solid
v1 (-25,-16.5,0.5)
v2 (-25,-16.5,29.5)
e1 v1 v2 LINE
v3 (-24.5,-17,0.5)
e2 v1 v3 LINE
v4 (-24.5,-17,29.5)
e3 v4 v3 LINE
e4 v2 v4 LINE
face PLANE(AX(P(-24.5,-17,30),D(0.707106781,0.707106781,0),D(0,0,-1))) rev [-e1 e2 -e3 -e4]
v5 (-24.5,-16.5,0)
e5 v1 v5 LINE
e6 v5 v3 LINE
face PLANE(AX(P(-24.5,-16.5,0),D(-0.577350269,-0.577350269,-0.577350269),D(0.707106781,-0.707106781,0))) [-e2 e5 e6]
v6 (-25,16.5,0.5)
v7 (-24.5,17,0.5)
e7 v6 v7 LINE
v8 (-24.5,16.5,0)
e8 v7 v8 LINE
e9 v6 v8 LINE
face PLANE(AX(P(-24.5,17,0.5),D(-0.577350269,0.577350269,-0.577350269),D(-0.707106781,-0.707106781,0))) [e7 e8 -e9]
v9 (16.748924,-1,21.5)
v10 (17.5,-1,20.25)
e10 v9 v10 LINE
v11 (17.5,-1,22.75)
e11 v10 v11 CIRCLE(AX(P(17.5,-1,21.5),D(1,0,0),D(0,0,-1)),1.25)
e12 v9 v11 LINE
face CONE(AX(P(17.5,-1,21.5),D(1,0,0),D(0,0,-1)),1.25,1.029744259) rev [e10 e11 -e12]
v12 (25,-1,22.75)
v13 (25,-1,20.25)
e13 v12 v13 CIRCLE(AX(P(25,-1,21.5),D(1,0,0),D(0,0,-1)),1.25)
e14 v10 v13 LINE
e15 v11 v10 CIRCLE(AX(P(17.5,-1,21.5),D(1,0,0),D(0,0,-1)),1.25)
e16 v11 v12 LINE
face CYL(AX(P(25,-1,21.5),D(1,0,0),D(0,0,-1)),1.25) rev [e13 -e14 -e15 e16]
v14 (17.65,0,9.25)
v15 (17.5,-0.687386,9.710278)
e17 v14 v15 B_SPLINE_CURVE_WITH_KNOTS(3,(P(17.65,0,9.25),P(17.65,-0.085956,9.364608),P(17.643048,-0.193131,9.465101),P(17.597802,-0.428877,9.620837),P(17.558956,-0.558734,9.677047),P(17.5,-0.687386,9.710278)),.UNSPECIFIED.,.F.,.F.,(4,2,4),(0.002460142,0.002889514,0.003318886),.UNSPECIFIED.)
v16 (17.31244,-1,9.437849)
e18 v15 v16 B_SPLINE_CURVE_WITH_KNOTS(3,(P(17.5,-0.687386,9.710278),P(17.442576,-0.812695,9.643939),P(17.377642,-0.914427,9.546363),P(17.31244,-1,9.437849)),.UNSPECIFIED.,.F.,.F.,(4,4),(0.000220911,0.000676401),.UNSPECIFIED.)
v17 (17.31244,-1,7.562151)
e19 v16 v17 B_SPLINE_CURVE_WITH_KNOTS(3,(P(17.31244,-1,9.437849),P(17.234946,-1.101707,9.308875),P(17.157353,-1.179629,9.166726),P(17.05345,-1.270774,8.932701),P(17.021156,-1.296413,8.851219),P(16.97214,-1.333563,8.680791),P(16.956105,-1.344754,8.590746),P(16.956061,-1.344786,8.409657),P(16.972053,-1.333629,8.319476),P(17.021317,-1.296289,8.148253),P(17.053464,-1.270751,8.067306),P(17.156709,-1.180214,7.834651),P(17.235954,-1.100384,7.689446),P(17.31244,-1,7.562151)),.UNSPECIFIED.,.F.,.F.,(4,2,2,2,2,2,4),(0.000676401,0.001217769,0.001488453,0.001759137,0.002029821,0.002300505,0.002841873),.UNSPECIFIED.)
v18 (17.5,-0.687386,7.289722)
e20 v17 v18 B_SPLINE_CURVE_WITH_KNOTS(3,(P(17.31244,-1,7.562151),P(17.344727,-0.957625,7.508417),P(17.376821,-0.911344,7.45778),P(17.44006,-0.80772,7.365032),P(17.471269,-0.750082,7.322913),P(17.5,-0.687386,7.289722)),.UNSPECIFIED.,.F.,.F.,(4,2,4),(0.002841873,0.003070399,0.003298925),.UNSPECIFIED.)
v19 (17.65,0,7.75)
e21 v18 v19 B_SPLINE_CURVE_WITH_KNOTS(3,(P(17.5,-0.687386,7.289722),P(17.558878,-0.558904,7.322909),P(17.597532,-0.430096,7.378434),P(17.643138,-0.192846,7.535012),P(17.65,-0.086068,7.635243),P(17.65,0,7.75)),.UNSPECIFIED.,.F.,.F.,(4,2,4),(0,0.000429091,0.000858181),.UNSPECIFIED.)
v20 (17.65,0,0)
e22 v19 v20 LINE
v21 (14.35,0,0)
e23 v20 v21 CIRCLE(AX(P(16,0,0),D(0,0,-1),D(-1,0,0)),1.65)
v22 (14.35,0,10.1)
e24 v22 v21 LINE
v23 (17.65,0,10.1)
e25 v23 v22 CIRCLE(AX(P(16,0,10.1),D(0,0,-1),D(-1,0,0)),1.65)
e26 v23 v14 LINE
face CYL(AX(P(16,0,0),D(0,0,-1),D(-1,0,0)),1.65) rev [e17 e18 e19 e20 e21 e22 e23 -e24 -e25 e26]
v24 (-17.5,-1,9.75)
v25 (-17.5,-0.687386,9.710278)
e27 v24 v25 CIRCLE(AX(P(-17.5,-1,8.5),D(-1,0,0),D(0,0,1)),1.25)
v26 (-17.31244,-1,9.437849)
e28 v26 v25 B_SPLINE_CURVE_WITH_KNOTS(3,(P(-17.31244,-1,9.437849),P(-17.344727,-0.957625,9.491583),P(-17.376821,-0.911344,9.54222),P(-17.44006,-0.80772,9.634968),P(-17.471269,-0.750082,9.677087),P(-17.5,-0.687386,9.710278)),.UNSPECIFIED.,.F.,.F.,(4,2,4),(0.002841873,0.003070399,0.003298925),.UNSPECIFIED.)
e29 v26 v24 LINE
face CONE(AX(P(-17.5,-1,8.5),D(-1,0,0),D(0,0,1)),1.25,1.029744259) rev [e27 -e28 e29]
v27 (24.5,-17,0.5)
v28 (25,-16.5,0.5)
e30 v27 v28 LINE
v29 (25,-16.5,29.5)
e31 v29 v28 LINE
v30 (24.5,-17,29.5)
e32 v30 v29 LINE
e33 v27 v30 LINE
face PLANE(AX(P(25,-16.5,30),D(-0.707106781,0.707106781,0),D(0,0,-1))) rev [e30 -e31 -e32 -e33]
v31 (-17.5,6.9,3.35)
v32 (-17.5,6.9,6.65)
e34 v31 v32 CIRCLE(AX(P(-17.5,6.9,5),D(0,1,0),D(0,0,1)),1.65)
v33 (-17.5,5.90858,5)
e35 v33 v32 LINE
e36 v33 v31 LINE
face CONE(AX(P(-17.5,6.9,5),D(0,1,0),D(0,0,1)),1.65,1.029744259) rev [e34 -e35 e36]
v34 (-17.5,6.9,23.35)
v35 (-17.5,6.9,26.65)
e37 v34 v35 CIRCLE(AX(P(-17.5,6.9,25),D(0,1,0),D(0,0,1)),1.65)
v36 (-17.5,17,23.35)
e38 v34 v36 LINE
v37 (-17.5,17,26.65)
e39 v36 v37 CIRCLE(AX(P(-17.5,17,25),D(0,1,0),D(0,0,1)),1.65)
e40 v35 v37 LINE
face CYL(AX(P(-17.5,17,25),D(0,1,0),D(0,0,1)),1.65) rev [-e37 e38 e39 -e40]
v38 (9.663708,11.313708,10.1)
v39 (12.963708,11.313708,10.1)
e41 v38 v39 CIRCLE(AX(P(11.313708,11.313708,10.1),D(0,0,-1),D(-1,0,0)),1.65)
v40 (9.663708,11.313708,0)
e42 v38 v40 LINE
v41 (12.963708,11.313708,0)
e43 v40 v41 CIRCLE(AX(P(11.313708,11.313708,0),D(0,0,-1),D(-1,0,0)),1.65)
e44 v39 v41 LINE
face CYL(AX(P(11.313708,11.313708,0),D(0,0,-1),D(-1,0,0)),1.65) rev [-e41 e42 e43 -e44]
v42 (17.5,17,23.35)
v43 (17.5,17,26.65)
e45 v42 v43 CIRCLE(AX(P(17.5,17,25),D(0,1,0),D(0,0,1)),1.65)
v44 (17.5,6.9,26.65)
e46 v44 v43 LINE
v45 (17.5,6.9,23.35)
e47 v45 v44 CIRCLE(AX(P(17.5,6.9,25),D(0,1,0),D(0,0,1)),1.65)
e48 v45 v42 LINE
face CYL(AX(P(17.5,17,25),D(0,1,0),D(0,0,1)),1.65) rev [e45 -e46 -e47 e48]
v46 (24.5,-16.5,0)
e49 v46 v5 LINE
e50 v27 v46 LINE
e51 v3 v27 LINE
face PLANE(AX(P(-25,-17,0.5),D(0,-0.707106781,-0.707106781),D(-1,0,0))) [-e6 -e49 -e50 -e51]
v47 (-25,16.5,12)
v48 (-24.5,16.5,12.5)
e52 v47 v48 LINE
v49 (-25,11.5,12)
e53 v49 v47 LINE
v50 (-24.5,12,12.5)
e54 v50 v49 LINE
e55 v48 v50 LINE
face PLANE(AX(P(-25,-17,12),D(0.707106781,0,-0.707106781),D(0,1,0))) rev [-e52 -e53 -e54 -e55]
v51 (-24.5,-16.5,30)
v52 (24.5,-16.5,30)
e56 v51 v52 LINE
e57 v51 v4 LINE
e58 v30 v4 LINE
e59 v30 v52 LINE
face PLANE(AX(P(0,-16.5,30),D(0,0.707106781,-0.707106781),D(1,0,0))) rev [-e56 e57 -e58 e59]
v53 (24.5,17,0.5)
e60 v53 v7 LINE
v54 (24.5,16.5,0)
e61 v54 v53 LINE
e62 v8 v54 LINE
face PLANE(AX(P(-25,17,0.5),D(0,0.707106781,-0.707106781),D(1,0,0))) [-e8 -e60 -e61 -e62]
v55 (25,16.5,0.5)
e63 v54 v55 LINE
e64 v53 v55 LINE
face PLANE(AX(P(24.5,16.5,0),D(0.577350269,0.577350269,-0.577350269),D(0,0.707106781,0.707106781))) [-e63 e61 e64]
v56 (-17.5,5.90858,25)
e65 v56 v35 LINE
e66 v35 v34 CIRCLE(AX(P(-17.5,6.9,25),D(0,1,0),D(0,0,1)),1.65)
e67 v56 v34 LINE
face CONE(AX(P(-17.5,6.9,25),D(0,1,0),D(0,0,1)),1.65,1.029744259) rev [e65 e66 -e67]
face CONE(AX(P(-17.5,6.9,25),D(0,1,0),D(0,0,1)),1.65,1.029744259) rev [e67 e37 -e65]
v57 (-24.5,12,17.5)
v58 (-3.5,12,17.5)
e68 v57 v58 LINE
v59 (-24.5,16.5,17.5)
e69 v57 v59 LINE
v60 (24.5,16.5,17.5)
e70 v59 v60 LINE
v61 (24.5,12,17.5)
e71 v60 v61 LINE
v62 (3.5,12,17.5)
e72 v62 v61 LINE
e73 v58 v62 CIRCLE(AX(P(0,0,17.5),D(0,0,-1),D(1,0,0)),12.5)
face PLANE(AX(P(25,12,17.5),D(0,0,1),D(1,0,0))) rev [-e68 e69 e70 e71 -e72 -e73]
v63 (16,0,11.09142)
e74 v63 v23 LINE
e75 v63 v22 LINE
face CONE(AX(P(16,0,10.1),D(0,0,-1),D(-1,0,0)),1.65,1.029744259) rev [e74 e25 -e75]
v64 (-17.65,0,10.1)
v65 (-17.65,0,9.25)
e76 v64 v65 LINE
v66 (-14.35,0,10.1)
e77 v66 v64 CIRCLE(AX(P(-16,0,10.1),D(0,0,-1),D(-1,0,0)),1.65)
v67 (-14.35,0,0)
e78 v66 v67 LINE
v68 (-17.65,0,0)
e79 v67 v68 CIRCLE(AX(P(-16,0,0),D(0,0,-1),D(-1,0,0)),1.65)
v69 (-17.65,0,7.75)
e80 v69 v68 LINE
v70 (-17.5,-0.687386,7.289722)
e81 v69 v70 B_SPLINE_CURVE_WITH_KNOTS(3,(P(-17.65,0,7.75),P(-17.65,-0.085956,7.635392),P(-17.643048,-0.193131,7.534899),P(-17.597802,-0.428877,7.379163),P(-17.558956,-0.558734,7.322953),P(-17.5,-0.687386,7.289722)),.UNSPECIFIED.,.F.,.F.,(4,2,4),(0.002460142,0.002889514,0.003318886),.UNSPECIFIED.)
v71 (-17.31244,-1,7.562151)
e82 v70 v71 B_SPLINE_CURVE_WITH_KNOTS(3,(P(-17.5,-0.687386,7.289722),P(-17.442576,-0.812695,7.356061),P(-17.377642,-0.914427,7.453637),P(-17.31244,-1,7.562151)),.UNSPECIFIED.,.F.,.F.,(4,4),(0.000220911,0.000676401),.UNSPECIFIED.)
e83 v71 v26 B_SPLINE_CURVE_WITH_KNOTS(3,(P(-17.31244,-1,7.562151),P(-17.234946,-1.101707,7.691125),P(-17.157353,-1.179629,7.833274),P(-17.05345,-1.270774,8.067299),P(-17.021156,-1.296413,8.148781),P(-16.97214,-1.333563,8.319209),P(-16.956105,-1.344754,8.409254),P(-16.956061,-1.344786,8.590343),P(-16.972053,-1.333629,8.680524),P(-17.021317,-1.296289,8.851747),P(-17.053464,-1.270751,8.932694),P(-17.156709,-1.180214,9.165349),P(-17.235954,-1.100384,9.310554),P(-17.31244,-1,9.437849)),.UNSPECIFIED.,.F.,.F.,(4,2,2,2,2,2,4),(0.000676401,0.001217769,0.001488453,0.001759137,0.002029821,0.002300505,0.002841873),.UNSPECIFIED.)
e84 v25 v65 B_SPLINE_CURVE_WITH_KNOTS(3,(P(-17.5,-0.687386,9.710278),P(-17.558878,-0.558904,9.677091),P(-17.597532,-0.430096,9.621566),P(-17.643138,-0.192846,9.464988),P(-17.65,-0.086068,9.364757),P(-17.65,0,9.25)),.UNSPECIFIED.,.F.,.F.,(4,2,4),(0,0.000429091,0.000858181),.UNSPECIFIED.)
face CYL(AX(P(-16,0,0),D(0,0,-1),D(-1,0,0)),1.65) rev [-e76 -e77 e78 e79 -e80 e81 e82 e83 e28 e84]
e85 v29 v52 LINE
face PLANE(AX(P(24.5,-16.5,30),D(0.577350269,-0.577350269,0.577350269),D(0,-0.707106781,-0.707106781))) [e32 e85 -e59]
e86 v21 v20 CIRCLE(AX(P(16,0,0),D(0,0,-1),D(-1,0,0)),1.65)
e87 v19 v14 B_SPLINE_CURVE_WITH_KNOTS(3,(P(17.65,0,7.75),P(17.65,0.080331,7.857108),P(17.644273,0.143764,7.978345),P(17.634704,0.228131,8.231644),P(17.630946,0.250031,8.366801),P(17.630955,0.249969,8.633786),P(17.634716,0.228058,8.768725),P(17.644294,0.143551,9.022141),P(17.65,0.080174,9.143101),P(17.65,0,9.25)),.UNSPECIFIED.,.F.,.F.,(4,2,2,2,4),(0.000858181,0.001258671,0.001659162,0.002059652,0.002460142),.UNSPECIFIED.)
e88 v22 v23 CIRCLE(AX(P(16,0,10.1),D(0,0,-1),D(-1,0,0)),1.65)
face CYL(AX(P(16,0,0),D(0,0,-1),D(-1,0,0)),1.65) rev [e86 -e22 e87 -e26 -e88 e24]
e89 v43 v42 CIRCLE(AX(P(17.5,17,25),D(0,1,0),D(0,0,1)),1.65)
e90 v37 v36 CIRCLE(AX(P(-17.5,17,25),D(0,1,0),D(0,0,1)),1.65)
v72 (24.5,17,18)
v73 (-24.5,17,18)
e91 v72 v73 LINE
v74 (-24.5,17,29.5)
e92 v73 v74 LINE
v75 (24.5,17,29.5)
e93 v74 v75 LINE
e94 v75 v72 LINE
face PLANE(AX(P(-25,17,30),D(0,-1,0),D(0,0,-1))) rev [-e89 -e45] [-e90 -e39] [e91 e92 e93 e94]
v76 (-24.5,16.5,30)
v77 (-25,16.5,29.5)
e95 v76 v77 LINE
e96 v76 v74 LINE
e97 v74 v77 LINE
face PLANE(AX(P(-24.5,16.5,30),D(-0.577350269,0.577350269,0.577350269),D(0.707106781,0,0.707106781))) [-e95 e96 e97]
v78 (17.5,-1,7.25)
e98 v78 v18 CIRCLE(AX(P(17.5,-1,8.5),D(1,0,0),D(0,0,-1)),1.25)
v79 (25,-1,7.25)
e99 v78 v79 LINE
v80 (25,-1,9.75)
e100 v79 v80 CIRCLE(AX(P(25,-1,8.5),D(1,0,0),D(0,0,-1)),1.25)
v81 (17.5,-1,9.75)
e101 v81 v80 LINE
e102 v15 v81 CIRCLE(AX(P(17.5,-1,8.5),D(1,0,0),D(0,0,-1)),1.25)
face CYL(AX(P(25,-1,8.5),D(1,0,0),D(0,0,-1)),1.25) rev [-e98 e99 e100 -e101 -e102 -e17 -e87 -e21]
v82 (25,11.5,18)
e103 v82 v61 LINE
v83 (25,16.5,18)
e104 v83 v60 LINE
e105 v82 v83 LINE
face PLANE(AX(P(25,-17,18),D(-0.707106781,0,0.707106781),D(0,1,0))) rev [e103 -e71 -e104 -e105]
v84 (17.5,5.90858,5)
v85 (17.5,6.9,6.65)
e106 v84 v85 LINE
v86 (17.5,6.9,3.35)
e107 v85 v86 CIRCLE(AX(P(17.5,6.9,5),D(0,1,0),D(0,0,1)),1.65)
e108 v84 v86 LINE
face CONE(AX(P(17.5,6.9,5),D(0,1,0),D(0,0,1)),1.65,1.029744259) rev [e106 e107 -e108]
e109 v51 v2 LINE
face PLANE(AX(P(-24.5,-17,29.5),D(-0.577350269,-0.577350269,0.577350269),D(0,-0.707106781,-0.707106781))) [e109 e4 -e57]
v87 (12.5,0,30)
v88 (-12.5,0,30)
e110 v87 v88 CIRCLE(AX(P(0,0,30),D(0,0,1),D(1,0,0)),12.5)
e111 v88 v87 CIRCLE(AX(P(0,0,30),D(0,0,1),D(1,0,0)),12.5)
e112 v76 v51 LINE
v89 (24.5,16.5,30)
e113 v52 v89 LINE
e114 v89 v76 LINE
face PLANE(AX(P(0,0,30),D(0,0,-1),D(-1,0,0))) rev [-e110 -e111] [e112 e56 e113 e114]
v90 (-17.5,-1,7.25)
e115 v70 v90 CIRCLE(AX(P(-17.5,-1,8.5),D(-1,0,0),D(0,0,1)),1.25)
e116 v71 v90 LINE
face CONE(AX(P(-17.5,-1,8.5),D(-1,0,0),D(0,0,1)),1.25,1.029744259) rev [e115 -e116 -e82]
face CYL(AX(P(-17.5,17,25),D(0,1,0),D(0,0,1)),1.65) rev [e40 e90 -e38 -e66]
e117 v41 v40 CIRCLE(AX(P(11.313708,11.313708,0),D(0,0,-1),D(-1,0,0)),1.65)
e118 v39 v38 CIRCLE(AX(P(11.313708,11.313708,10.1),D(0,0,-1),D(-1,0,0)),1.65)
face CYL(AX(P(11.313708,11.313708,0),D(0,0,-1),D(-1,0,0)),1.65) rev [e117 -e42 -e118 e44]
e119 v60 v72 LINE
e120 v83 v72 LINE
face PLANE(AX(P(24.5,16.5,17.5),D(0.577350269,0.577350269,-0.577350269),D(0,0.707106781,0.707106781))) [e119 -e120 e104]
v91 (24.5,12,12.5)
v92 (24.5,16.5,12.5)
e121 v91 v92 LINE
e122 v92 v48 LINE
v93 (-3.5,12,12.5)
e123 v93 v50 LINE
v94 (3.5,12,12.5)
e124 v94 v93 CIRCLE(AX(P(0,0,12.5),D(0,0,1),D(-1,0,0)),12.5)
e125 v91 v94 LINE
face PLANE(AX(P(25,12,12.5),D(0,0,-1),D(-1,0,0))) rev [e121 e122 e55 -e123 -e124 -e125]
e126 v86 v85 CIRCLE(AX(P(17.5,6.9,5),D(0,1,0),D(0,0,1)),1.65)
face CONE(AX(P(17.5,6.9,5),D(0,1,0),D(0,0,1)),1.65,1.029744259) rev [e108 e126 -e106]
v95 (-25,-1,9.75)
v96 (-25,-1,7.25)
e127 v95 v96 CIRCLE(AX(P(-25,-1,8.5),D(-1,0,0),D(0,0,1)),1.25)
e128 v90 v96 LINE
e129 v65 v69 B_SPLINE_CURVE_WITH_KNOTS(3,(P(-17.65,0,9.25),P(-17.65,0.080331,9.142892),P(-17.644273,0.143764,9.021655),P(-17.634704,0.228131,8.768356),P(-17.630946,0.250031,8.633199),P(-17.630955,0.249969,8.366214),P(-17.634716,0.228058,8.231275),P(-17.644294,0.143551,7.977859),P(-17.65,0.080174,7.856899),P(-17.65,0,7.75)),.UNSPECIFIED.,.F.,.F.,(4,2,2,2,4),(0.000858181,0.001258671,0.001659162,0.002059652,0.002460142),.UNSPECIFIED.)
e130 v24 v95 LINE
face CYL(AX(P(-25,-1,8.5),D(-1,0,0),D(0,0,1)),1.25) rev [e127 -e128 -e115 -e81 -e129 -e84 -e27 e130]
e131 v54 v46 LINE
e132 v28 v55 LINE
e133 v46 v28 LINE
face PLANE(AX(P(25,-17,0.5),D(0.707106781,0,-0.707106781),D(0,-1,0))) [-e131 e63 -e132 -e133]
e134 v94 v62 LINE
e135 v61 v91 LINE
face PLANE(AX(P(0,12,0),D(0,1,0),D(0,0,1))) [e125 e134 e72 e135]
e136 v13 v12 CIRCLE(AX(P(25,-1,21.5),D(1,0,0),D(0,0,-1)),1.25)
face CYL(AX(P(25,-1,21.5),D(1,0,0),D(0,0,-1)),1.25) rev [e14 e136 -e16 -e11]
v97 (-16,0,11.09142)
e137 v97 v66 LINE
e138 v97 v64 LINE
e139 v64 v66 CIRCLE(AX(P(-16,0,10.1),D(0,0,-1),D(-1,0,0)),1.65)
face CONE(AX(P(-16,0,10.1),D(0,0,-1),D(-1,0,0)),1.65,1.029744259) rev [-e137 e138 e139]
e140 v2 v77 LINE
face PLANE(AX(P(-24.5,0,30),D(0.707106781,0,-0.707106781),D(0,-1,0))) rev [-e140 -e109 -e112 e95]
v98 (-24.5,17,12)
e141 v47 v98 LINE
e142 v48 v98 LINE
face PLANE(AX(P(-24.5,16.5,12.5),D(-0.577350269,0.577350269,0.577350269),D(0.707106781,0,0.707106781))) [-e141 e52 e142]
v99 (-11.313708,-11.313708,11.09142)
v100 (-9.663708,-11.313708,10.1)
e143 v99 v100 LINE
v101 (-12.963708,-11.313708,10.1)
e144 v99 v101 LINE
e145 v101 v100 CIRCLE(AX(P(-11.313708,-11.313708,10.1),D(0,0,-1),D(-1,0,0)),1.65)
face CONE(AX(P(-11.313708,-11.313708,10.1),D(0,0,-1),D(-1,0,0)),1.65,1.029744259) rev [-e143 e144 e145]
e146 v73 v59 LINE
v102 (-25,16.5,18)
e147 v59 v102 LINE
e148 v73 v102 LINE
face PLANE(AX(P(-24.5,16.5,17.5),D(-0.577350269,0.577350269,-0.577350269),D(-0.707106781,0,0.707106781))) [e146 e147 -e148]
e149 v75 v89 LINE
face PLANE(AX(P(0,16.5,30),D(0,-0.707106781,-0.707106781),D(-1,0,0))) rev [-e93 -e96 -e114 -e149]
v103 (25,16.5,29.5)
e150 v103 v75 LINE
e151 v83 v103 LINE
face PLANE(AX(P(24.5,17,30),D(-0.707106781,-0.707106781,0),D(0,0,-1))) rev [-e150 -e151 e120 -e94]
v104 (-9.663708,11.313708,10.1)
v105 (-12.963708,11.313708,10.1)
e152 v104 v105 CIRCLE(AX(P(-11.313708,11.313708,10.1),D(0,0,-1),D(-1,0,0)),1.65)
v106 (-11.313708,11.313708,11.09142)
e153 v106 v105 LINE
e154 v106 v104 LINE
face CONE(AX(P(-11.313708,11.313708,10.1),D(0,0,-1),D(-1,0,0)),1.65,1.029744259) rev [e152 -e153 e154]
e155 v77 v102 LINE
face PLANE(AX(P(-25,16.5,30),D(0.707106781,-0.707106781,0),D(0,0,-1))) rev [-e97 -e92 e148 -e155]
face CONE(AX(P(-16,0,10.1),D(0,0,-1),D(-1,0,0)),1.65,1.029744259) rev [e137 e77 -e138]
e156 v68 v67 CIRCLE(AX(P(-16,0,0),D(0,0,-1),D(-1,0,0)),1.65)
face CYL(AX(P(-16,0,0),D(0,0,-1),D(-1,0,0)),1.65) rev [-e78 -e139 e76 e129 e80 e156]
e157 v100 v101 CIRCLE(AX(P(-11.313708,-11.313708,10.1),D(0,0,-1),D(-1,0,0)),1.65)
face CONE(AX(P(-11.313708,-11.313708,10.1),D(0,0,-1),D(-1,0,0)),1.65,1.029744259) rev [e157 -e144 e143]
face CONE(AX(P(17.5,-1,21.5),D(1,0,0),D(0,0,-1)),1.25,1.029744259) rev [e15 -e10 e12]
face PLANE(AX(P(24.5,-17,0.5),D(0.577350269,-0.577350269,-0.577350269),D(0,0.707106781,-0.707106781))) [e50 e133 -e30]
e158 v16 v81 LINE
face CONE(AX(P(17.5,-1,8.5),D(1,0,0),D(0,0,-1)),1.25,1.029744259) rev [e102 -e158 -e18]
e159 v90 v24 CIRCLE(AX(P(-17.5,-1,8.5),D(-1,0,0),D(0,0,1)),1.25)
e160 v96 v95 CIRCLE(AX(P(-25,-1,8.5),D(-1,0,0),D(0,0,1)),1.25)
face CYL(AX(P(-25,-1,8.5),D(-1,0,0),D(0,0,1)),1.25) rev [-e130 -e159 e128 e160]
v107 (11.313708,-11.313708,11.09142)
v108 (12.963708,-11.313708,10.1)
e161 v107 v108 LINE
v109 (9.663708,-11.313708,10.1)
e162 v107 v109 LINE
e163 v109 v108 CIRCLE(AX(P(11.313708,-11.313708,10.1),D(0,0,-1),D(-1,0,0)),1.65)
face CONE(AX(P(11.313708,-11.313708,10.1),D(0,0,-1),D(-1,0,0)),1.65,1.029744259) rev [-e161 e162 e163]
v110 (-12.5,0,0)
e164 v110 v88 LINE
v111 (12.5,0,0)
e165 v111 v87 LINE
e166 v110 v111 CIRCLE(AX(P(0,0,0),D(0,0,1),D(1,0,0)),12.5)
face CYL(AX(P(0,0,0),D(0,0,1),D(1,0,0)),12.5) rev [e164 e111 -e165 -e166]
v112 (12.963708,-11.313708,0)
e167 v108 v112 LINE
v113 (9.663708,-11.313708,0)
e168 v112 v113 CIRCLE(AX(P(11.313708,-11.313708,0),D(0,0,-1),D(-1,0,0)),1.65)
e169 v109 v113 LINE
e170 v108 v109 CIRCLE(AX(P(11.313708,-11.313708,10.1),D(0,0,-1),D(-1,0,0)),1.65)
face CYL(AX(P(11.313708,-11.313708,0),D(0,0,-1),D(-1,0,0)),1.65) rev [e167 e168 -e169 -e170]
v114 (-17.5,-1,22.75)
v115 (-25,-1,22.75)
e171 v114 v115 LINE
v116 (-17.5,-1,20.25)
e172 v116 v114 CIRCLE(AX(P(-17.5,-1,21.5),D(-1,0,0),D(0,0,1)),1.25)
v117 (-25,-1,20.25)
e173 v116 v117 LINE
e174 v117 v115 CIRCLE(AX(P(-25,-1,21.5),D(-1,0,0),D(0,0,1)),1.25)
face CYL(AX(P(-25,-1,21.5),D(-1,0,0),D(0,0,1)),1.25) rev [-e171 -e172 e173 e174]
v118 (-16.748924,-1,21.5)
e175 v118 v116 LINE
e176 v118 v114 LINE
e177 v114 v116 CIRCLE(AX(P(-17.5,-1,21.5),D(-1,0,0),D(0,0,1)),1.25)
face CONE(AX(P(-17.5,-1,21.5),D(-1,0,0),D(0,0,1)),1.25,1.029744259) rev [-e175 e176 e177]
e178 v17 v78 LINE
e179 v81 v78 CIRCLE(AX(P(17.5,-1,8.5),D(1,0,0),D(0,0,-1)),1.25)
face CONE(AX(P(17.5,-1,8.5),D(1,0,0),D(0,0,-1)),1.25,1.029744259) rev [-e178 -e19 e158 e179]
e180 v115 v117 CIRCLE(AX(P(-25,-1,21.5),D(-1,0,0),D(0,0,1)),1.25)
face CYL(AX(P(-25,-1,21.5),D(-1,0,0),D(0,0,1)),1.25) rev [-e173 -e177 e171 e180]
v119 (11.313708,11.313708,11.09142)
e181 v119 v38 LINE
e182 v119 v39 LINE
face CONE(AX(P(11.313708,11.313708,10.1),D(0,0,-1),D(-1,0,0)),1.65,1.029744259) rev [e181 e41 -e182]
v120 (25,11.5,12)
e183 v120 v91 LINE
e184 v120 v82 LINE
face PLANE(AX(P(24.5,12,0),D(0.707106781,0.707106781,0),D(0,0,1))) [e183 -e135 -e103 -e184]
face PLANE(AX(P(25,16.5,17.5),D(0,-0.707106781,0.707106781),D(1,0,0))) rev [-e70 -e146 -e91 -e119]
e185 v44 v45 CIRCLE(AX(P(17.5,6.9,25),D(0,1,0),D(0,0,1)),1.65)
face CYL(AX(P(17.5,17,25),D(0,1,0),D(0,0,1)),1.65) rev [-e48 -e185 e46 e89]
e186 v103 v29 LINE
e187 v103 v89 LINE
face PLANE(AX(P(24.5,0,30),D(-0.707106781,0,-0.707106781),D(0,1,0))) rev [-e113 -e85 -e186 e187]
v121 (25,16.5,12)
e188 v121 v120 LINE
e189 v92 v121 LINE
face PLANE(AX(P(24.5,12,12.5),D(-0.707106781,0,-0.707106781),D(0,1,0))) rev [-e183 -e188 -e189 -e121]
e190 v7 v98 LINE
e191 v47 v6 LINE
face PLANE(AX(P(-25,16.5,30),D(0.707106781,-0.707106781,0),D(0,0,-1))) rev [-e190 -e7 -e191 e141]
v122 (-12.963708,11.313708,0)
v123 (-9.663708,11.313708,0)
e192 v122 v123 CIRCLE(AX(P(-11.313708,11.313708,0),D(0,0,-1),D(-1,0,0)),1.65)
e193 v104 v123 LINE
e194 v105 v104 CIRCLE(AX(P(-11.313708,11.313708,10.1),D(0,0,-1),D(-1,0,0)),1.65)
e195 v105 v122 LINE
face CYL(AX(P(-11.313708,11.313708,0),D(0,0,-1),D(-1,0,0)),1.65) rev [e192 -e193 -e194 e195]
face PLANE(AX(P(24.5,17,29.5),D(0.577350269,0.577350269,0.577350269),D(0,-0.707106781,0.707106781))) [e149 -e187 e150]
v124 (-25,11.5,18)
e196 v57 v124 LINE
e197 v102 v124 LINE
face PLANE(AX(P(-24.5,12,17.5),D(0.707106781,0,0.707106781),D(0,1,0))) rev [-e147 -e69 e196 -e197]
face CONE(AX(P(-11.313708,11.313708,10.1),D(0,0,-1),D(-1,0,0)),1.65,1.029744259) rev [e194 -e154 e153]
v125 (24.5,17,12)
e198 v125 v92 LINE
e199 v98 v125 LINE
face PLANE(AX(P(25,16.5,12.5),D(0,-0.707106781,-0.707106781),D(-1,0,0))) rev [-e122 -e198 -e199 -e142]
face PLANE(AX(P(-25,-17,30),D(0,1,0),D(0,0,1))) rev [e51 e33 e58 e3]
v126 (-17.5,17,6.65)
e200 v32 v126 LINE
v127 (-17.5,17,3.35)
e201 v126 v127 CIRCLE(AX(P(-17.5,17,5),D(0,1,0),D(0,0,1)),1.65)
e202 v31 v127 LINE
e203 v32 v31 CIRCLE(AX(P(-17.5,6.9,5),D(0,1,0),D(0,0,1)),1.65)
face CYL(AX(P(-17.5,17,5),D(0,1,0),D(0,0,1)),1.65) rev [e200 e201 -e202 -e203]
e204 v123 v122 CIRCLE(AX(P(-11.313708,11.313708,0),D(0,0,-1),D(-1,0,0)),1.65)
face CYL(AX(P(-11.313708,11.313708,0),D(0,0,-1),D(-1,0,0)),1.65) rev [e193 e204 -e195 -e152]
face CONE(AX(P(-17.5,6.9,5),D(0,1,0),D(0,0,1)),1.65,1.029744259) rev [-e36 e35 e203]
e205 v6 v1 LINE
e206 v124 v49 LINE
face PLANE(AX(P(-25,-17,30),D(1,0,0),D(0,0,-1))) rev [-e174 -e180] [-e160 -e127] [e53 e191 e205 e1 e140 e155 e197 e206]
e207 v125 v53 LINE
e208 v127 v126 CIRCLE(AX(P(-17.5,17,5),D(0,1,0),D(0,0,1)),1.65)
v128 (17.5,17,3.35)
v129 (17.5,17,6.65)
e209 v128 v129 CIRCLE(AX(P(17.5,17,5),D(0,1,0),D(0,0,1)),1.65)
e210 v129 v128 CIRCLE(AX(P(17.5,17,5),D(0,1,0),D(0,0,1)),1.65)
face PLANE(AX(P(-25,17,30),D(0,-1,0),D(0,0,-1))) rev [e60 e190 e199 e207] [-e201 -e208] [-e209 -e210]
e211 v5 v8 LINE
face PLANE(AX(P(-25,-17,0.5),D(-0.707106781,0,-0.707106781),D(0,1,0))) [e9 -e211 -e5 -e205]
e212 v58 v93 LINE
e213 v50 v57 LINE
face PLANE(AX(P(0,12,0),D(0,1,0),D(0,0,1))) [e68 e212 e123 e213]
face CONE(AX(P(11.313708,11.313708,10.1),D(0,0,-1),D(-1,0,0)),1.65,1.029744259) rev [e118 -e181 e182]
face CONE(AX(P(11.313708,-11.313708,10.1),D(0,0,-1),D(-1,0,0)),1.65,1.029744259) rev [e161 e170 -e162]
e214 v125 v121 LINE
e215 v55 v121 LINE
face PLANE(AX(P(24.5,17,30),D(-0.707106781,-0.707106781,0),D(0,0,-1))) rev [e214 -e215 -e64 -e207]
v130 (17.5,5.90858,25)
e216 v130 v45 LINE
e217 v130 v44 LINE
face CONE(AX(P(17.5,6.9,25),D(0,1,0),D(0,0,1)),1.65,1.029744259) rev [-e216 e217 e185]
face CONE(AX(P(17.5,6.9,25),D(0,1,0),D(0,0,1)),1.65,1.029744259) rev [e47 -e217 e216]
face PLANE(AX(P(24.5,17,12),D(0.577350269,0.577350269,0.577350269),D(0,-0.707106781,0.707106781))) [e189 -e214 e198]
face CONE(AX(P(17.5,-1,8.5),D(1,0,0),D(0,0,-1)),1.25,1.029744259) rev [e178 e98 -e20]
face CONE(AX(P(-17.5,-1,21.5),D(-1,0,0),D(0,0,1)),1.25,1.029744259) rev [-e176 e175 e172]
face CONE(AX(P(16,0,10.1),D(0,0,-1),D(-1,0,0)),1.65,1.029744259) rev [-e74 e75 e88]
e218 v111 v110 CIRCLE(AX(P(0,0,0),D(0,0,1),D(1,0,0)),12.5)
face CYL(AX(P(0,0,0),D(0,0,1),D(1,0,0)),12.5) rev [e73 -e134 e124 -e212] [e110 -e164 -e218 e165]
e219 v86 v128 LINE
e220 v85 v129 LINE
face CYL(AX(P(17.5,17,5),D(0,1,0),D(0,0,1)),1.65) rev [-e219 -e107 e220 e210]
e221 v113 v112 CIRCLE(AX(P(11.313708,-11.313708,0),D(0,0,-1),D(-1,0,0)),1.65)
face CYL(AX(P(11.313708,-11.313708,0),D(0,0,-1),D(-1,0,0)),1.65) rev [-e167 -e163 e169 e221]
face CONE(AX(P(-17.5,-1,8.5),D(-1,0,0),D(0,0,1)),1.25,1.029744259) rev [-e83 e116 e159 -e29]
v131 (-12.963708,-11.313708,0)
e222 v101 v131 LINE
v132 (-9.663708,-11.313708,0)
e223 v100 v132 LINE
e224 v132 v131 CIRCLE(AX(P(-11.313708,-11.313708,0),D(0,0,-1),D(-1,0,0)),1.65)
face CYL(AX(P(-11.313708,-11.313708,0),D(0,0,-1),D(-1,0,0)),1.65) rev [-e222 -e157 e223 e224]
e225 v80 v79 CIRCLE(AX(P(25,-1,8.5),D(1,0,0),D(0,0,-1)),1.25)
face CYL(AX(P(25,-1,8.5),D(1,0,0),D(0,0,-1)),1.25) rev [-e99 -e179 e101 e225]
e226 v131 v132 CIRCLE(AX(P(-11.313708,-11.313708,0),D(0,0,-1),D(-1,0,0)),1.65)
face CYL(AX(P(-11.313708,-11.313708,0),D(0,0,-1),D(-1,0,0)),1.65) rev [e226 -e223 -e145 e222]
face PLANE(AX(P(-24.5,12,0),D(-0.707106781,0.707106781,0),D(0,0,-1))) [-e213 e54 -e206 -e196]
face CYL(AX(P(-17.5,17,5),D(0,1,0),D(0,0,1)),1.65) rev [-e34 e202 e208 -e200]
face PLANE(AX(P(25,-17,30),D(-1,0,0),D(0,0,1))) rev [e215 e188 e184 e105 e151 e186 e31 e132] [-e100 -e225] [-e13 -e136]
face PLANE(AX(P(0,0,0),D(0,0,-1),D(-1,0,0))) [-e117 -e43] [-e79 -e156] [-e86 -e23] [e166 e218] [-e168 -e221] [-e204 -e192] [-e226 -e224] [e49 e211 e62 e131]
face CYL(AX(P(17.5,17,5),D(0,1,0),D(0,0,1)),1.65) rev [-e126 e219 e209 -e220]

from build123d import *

# Parameters (mm, degrees)
SKETCH_1_W                  = 50
SKETCH_1_H                  = 34
EXTRUDE_1_DEPTH             = 30
HOLE_WIZARD_M4_1_D          = 3.3
HOLE_WIZARD_M4_1_DEPTH      = 10.1
HOLE_WIZARD_M4_1_TIP        = 0.991420021
HOLE_WIZARD_M3_1_AT_2_COUNT = 2
HOLE_WIZARD_M3_1_AT_2_PITCH = 13
SKETCH_15_R                 = 12.5
CUT_EXTRUDE_1_DEPTH         = 43.591079007
HOLE_WIZARD_M4_2_D          = 3.3
HOLE_WIZARD_M4_2_DEPTH      = 10.1
HOLE_WIZARD_M4_2_TIP        = 0.991420021
SKETCH_18_W                 = 50
SKETCH_18_H                 = 5
CUT_EXTRUDE_2_DEPTH         = 5
CHAMFER_1_SIZE              = 0.5


with BuildPart() as part:
    # 草图1 → 凸台-拉伸1 (new body)
    with BuildSketch(Plane.XY):
        Rectangle(SKETCH_1_W, SKETCH_1_H)
    extrude(amount=EXTRUDE_1_DEPTH)

    # M4 螺纹孔1
    with Locations(Plane(origin=(0, 0, 0), x_dir=(-1, 0, 0), z_dir=(0, 0, -1))):
        with Locations((-11.313708499, -11.313708499), (-16, 0), (-11.313708499, 11.313708499), (11.313708499, 11.313708499), (16, 0), (11.313708499, -11.313708499)):
            Hole(HOLE_WIZARD_M4_1_D / 2, depth=HOLE_WIZARD_M4_1_DEPTH)
            with Locations((0, 0, -(HOLE_WIZARD_M4_1_DEPTH + HOLE_WIZARD_M4_1_TIP / 2))):  # 118° drill point
                Cone(0, HOLE_WIZARD_M4_1_D / 2, HOLE_WIZARD_M4_1_TIP, mode=Mode.SUBTRACT)

    # 草图12 → M3 螺纹孔1 (revolve, cut)
    with BuildSketch(Plane(origin=(-25, -1, 8.5), x_dir=(0, 0, 1), z_dir=(0, 1, 0))):
        Polygon((0, 0), (0, 8.251075774), (1.25, 7.5), (1.25, 0), align=None)
    hole_wizard_m3_1 = revolve(axis=Axis((-31.35, -1, 8.5), (1, 0, 0)), mode=Mode.SUBTRACT)

    # M3 螺纹孔1 at 2: M3 螺纹孔1 ×2
    with Locations(*[(0, 0, i * HOLE_WIZARD_M3_1_AT_2_PITCH) for i in range(1, HOLE_WIZARD_M3_1_AT_2_COUNT)]):
        add(hole_wizard_m3_1, mode=Mode.SUBTRACT)

    # 镜向1: M3 螺纹孔1 across plane
    add(hole_wizard_m3_1.mirror(Plane(origin=(0, 0, 0), x_dir=(0, 0, 1), z_dir=(1, 0, 0))), mode=Mode.SUBTRACT)

    # 镜向1 copy 1 sketch → 镜向1 copy 1 (revolve, cut)
    with BuildSketch(Plane(origin=(25, -1, 21.5), x_dir=(0, 0, 1), z_dir=(0, 1, 0))):
        Polygon((0, 0), (0, -8.251075774), (1.25, -7.5), (1.25, 0), align=None)
    revolve(axis=Axis((31.35, -1, 21.5), (1, 0, 0)), mode=Mode.SUBTRACT)

    # 草图15 → 切除-拉伸1 (cut, through all)
    with BuildSketch(Plane.XY.offset(30)):
        Circle(SKETCH_15_R)
    extrude(amount=-CUT_EXTRUDE_1_DEPTH, mode=Mode.SUBTRACT)

    # M4 螺纹孔2
    with Locations(Plane(origin=(0, 17, 0), x_dir=(1, 0, 0), z_dir=(0, 1, 0))):
        with Locations((17.5, -25), (-17.5, -25), (-17.5, -5), (17.5, -5)):
            Hole(HOLE_WIZARD_M4_2_D / 2, depth=HOLE_WIZARD_M4_2_DEPTH)
            with Locations((0, 0, -(HOLE_WIZARD_M4_2_DEPTH + HOLE_WIZARD_M4_2_TIP / 2))):  # 118° drill point
                Cone(0, HOLE_WIZARD_M4_2_D / 2, HOLE_WIZARD_M4_2_TIP, mode=Mode.SUBTRACT)

    # 草图18 → 切除-拉伸2 (cut)
    with BuildSketch(Plane(origin=(0, 17, 0), x_dir=(1, 0, 0), z_dir=(0, 1, 0))):
        with Locations((0, -15)):
            Rectangle(SKETCH_18_W, SKETCH_18_H)
    extrude(amount=-CUT_EXTRUDE_2_DEPTH, mode=Mode.SUBTRACT)

    # 倒角1
    chamfer_1_edges = [part.edges().sort_by_distance(p)[0] for p in [
        (-25, 0, 30),
        (0, 17, 17.5),
        (0, -17, 30),
        (25, 0, 30),
        (0, -17, 0),
        (-25, 0, 0),
        (0, 17, 0),
        (25, 0, 0),
        (0, 17, 30),
        (25, -17, 15),
        (-25, -17, 15),
        (-25, 17, 23.75),
        (25, 17, 23.75),
        (-25, 17, 6.25),
        (25, 17, 6.25),
        (25, 14.5, 17.5),
        (-25, 14.5, 12.5),
        (25, 12, 15),
        (25, 14.5, 12.5),
        (-25, 12, 15),
        (-25, 14.5, 17.5),
        (0, 17, 12.5),
    ]]
    chamfer(chamfer_1_edges, length=CHAMFER_1_SIZE)


solid = part.part
